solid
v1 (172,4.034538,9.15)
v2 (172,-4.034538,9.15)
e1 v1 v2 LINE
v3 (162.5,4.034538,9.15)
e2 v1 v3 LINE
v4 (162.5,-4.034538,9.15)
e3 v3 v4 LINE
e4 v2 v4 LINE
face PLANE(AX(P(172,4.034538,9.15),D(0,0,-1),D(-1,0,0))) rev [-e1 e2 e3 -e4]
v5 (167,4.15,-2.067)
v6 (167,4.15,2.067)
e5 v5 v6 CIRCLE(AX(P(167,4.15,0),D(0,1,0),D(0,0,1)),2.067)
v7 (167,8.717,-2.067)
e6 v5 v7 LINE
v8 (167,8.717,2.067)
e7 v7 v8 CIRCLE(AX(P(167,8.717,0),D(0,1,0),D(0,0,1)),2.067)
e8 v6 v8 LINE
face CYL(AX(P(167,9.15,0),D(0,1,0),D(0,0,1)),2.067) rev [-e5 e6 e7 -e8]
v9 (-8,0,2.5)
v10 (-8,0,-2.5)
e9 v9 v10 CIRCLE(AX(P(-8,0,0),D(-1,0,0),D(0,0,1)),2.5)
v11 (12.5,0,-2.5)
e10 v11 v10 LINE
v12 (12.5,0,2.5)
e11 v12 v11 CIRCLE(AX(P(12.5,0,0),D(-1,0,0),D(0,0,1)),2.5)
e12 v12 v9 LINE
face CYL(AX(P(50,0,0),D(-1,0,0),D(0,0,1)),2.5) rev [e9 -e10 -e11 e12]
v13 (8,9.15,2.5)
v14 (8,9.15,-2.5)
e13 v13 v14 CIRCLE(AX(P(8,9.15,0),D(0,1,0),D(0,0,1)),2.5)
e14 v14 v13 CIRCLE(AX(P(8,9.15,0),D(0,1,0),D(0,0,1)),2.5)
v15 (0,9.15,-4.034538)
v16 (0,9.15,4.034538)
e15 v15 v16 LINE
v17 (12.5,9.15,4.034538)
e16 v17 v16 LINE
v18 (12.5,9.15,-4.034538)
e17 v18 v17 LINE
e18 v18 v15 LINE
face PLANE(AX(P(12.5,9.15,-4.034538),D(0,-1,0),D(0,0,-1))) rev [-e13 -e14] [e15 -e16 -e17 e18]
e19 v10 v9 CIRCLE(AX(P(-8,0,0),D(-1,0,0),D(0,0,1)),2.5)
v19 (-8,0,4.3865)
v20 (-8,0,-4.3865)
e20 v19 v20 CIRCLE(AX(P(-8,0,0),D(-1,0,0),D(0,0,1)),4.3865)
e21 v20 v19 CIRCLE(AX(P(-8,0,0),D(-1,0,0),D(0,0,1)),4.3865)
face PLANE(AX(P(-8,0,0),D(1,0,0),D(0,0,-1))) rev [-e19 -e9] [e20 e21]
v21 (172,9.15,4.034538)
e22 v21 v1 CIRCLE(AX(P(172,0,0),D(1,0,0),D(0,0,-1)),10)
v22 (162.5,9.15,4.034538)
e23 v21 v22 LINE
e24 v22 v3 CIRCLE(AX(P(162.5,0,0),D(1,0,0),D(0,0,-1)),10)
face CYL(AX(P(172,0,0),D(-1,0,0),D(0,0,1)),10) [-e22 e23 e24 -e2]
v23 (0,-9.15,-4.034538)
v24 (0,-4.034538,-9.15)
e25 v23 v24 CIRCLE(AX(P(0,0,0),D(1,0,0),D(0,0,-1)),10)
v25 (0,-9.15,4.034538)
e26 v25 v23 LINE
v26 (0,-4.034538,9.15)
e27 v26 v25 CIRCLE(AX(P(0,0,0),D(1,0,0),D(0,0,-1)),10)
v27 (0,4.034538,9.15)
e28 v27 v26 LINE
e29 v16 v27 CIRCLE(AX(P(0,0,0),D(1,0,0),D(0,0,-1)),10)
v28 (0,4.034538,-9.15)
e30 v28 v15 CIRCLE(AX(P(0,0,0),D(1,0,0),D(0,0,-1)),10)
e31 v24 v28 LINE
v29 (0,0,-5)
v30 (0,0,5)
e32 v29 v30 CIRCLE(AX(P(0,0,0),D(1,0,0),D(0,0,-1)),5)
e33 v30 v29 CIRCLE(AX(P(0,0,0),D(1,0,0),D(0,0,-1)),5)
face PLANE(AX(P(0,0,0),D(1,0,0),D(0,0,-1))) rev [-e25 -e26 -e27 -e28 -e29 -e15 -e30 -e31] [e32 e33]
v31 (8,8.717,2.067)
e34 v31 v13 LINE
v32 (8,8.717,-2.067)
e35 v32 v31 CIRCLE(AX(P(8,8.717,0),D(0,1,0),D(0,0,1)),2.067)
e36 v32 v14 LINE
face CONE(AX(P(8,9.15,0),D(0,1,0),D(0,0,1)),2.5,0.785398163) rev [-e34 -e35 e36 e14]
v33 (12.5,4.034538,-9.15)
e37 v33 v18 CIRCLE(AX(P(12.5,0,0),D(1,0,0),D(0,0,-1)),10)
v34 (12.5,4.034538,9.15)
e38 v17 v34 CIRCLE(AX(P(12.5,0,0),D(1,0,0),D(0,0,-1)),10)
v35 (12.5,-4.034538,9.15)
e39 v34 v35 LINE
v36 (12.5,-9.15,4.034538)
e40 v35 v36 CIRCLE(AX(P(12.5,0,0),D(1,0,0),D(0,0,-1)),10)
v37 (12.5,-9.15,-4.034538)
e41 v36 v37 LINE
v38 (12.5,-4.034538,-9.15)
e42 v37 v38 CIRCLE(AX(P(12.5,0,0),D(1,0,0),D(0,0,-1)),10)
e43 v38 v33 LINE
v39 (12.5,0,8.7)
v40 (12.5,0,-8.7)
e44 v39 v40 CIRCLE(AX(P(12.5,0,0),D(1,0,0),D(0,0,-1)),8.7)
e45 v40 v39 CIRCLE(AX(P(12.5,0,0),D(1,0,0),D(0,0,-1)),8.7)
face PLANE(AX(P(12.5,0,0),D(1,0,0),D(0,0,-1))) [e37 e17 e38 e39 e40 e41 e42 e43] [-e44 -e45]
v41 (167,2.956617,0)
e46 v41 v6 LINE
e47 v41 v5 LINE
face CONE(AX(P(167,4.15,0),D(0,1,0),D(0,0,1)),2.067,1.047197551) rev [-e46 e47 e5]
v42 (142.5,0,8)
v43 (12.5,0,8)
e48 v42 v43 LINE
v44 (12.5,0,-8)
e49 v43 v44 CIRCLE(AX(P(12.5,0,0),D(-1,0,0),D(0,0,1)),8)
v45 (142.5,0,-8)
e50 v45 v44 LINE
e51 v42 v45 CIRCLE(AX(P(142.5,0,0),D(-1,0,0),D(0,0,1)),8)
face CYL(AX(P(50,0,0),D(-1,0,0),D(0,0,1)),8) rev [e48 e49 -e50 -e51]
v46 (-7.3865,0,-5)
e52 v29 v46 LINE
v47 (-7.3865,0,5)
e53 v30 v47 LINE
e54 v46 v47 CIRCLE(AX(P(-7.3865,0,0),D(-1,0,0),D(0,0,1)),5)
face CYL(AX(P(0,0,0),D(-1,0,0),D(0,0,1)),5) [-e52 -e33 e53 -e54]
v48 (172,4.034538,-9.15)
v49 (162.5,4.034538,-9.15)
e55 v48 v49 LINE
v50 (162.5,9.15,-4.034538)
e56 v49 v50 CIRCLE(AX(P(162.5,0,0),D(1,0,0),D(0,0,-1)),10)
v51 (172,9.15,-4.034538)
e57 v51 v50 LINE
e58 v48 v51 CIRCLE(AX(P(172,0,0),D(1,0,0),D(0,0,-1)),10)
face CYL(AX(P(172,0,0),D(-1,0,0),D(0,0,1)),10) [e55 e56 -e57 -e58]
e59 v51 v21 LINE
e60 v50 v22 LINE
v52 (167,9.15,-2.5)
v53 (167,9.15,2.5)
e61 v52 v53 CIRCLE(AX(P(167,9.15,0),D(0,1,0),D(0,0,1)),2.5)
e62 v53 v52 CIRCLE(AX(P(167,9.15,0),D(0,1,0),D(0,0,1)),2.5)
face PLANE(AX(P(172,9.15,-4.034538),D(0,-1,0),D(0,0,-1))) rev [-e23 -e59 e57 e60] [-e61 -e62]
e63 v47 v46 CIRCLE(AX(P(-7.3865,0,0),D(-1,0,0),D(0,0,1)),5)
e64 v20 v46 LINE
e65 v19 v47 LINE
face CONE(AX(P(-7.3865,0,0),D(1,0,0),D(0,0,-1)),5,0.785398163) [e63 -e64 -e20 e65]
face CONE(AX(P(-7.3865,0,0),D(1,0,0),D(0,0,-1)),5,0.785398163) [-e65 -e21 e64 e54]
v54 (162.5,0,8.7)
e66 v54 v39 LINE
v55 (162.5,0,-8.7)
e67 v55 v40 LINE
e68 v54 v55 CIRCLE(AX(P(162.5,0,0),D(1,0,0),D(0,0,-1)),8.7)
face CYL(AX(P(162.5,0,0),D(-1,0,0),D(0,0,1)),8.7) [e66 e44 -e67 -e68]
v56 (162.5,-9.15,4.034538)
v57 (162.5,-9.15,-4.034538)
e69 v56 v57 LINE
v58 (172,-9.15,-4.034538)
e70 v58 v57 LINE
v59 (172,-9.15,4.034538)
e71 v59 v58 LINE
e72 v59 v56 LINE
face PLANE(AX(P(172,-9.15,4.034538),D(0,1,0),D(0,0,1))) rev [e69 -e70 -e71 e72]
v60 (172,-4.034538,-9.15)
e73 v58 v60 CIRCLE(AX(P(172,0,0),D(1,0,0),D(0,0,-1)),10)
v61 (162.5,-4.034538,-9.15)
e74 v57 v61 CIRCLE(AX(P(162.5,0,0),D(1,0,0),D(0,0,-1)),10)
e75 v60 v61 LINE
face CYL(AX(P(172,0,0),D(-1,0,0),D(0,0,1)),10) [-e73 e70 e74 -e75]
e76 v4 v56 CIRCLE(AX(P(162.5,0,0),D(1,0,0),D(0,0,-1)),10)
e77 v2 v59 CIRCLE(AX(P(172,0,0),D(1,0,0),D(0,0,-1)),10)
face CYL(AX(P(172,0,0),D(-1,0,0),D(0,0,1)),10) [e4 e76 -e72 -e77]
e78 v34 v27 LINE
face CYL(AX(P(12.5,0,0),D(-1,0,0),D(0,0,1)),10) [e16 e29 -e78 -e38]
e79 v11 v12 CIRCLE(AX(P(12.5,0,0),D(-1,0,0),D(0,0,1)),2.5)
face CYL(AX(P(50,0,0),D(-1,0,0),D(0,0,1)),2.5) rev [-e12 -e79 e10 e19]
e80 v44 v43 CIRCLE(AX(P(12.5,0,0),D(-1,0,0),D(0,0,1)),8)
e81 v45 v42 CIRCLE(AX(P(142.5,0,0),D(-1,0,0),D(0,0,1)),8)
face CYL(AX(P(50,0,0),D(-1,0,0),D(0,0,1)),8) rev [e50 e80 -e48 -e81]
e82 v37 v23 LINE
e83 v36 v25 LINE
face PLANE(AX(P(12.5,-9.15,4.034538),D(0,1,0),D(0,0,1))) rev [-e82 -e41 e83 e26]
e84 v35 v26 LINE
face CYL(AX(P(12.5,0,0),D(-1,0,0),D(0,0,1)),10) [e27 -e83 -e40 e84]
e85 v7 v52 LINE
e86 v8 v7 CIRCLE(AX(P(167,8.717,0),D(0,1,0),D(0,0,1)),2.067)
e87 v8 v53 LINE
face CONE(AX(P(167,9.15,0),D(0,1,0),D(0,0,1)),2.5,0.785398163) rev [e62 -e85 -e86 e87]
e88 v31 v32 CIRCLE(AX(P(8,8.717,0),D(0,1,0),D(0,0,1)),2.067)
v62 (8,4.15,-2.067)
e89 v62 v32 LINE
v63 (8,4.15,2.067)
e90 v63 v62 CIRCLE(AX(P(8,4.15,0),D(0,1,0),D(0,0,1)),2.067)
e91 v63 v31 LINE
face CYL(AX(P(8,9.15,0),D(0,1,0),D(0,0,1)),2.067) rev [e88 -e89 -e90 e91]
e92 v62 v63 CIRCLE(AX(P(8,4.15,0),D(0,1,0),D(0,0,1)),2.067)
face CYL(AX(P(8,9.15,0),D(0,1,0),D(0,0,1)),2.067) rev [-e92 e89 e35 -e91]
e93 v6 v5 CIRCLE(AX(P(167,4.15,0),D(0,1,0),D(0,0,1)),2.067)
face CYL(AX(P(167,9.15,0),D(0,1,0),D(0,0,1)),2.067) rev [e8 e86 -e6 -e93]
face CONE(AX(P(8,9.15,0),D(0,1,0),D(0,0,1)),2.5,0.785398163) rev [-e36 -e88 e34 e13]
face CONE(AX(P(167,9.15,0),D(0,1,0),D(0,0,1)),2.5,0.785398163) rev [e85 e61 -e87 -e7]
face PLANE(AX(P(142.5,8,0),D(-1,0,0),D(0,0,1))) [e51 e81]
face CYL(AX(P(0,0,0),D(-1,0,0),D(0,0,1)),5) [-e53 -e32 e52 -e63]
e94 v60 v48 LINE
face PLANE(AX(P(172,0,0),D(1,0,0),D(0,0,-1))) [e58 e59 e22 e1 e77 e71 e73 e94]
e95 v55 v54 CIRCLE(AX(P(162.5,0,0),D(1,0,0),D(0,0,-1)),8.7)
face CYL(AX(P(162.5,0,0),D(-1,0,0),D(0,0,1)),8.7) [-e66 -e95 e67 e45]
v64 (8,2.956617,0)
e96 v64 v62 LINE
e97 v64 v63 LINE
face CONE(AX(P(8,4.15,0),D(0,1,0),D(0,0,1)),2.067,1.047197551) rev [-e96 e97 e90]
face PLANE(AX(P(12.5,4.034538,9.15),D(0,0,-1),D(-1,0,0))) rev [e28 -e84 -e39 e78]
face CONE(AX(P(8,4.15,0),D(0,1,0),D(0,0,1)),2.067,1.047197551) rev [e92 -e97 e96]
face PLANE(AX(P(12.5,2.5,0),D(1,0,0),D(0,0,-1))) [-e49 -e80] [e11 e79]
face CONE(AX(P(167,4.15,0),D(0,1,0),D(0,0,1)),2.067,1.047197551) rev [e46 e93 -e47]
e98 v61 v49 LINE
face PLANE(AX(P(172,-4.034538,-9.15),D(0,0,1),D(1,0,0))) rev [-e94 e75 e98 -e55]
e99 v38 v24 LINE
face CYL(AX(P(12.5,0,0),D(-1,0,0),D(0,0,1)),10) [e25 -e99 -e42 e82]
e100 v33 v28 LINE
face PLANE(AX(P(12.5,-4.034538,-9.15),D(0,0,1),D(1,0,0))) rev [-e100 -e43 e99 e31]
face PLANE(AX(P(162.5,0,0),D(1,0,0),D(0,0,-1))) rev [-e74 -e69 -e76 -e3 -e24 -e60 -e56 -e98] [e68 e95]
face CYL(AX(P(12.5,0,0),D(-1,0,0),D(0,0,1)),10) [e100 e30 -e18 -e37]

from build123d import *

# Parameters (mm, degrees)
BOSS_EXTRUDE1_DEPTH = 12.5
SKETCH3_R           = 8.7
BOSS_EXTRUDE2_DEPTH = 150
BOSS_EXTRUDE3_DEPTH = 9.5
HOLE1_D             = 4.134
HOLE1_DEPTH         = 5
HOLE1_CSINK_D       = 5
HOLE1_CSINK_ANGLE   = 90
HOLE1_TIP           = 1.193383006
HOLE2_D             = 4.134
HOLE2_DEPTH         = 5
HOLE2_CSINK_D       = 5
HOLE2_CSINK_ANGLE   = 90
HOLE2_TIP           = 1.193383006


with BuildPart() as part:
    # Sketch1 → Revolve1 (revolve)
    with BuildSketch(Plane.XY, mode=Mode.PRIVATE) as revolve1_sk:
        Polygon((-8, 0), (-8, 4.3865), (-7.3865, 5), (0, 5), (0, 0), align=None)
    revolve(revolve1_sk.sketch.rotate(Axis((0, 0, 0), (-1, 0, 0)), 270), axis=Axis((0, 0, 0), (-1, 0, 0)))

    # Sketch2 → Boss-Extrude1 (add)
    with BuildSketch(Plane(origin=(0, 0, 0), x_dir=(0, 0, -1), z_dir=(1, 0, 0))):
        with BuildLine():
            Line((-4.034538387, -9.15), (4.034538387, -9.15))
            ThreePointArc((4.034538387, -9.15), (7.071067812, -7.071067812), (9.15, -4.034538387))
            Line((9.15, -4.034538387), (9.15, 4.034538387))
            ThreePointArc((9.15, 4.034538387), (7.071067812, 7.071067812), (4.034538387, 9.15))
            Line((4.034538387, 9.15), (-4.034538387, 9.15))
            ThreePointArc((-4.034538387, 9.15), (-7.071067812, 7.071067812), (-9.15, 4.034538387))
            Line((-9.15, 4.034538387), (-9.15, -4.034538387))
            ThreePointArc((-9.15, -4.034538387), (-7.071067812, -7.071067812), (-4.034538387, -9.15))
        make_face()
    extrude(amount=BOSS_EXTRUDE1_DEPTH)

    # Sketch3 → Boss-Extrude2 (add)
    with BuildSketch(Plane(origin=(12.5, 0, 0), x_dir=(0, 0, -1), z_dir=(1, 0, 0))):
        Circle(SKETCH3_R)
    extrude(amount=BOSS_EXTRUDE2_DEPTH)

    # Sketch4 → Boss-Extrude3 (add)
    with BuildSketch(Plane(origin=(162.5, 0, 0), x_dir=(0, 0, -1), z_dir=(1, 0, 0))):
        with BuildLine():
            Line((-4.034538387, -9.15), (4.034538387, -9.15))
            ThreePointArc((4.034538387, -9.15), (7.071067812, -7.071067812), (9.15, -4.034538387))
            Line((9.15, -4.034538387), (9.15, 4.034538387))
            ThreePointArc((9.15, 4.034538387), (7.071067812, 7.071067812), (4.034538387, 9.15))
            Line((4.034538387, 9.15), (-4.034538387, 9.15))
            ThreePointArc((-4.034538387, 9.15), (-7.071067812, 7.071067812), (-9.15, 4.034538387))
            Line((-9.15, 4.034538387), (-9.15, -4.034538387))
            ThreePointArc((-9.15, -4.034538387), (-7.071067812, -7.071067812), (-4.034538387, -9.15))
        make_face()
    extrude(amount=BOSS_EXTRUDE3_DEPTH)

    # Hole1
    with Locations(Plane(origin=(0, 9.15, 0), x_dir=(1, 0, 0), z_dir=(0, 1, 0))):
        with Locations((8, 0)):
            CounterSinkHole(HOLE1_D / 2, HOLE1_CSINK_D / 2, depth=HOLE1_DEPTH, counter_sink_angle=HOLE1_CSINK_ANGLE)
            with Locations((0, 0, -(HOLE1_DEPTH + HOLE1_TIP / 2))):  # 120° drill point
                Cone(0, HOLE1_D / 2, HOLE1_TIP, mode=Mode.SUBTRACT)

    # Hole2
    with Locations(Plane(origin=(0, 9.15, 0), x_dir=(1, 0, 0), z_dir=(0, 1, 0))):
        with Locations((167, 0)):
            CounterSinkHole(HOLE2_D / 2, HOLE2_CSINK_D / 2, depth=HOLE2_DEPTH, counter_sink_angle=HOLE2_CSINK_ANGLE)
            with Locations((0, 0, -(HOLE2_DEPTH + HOLE2_TIP / 2))):  # 120° drill point
                Cone(0, HOLE2_D / 2, HOLE2_TIP, mode=Mode.SUBTRACT)

    # Sketch9 → Cut-Revolve1 (revolve, cut)
    with BuildSketch(Plane.XY, mode=Mode.PRIVATE) as cut_revolve1_sk:
        Polygon((-8, 0), (-8, 2.5), (12.5, 2.5), (12.5, 8), (142.5, 8), (142.5, 0), align=None)
    revolve(cut_revolve1_sk.sketch.rotate(Axis((50, 0, 0), (-1, 0, 0)), 270), axis=Axis((50, 0, 0), (-1, 0, 0)), mode=Mode.SUBTRACT)


solid = part.part
